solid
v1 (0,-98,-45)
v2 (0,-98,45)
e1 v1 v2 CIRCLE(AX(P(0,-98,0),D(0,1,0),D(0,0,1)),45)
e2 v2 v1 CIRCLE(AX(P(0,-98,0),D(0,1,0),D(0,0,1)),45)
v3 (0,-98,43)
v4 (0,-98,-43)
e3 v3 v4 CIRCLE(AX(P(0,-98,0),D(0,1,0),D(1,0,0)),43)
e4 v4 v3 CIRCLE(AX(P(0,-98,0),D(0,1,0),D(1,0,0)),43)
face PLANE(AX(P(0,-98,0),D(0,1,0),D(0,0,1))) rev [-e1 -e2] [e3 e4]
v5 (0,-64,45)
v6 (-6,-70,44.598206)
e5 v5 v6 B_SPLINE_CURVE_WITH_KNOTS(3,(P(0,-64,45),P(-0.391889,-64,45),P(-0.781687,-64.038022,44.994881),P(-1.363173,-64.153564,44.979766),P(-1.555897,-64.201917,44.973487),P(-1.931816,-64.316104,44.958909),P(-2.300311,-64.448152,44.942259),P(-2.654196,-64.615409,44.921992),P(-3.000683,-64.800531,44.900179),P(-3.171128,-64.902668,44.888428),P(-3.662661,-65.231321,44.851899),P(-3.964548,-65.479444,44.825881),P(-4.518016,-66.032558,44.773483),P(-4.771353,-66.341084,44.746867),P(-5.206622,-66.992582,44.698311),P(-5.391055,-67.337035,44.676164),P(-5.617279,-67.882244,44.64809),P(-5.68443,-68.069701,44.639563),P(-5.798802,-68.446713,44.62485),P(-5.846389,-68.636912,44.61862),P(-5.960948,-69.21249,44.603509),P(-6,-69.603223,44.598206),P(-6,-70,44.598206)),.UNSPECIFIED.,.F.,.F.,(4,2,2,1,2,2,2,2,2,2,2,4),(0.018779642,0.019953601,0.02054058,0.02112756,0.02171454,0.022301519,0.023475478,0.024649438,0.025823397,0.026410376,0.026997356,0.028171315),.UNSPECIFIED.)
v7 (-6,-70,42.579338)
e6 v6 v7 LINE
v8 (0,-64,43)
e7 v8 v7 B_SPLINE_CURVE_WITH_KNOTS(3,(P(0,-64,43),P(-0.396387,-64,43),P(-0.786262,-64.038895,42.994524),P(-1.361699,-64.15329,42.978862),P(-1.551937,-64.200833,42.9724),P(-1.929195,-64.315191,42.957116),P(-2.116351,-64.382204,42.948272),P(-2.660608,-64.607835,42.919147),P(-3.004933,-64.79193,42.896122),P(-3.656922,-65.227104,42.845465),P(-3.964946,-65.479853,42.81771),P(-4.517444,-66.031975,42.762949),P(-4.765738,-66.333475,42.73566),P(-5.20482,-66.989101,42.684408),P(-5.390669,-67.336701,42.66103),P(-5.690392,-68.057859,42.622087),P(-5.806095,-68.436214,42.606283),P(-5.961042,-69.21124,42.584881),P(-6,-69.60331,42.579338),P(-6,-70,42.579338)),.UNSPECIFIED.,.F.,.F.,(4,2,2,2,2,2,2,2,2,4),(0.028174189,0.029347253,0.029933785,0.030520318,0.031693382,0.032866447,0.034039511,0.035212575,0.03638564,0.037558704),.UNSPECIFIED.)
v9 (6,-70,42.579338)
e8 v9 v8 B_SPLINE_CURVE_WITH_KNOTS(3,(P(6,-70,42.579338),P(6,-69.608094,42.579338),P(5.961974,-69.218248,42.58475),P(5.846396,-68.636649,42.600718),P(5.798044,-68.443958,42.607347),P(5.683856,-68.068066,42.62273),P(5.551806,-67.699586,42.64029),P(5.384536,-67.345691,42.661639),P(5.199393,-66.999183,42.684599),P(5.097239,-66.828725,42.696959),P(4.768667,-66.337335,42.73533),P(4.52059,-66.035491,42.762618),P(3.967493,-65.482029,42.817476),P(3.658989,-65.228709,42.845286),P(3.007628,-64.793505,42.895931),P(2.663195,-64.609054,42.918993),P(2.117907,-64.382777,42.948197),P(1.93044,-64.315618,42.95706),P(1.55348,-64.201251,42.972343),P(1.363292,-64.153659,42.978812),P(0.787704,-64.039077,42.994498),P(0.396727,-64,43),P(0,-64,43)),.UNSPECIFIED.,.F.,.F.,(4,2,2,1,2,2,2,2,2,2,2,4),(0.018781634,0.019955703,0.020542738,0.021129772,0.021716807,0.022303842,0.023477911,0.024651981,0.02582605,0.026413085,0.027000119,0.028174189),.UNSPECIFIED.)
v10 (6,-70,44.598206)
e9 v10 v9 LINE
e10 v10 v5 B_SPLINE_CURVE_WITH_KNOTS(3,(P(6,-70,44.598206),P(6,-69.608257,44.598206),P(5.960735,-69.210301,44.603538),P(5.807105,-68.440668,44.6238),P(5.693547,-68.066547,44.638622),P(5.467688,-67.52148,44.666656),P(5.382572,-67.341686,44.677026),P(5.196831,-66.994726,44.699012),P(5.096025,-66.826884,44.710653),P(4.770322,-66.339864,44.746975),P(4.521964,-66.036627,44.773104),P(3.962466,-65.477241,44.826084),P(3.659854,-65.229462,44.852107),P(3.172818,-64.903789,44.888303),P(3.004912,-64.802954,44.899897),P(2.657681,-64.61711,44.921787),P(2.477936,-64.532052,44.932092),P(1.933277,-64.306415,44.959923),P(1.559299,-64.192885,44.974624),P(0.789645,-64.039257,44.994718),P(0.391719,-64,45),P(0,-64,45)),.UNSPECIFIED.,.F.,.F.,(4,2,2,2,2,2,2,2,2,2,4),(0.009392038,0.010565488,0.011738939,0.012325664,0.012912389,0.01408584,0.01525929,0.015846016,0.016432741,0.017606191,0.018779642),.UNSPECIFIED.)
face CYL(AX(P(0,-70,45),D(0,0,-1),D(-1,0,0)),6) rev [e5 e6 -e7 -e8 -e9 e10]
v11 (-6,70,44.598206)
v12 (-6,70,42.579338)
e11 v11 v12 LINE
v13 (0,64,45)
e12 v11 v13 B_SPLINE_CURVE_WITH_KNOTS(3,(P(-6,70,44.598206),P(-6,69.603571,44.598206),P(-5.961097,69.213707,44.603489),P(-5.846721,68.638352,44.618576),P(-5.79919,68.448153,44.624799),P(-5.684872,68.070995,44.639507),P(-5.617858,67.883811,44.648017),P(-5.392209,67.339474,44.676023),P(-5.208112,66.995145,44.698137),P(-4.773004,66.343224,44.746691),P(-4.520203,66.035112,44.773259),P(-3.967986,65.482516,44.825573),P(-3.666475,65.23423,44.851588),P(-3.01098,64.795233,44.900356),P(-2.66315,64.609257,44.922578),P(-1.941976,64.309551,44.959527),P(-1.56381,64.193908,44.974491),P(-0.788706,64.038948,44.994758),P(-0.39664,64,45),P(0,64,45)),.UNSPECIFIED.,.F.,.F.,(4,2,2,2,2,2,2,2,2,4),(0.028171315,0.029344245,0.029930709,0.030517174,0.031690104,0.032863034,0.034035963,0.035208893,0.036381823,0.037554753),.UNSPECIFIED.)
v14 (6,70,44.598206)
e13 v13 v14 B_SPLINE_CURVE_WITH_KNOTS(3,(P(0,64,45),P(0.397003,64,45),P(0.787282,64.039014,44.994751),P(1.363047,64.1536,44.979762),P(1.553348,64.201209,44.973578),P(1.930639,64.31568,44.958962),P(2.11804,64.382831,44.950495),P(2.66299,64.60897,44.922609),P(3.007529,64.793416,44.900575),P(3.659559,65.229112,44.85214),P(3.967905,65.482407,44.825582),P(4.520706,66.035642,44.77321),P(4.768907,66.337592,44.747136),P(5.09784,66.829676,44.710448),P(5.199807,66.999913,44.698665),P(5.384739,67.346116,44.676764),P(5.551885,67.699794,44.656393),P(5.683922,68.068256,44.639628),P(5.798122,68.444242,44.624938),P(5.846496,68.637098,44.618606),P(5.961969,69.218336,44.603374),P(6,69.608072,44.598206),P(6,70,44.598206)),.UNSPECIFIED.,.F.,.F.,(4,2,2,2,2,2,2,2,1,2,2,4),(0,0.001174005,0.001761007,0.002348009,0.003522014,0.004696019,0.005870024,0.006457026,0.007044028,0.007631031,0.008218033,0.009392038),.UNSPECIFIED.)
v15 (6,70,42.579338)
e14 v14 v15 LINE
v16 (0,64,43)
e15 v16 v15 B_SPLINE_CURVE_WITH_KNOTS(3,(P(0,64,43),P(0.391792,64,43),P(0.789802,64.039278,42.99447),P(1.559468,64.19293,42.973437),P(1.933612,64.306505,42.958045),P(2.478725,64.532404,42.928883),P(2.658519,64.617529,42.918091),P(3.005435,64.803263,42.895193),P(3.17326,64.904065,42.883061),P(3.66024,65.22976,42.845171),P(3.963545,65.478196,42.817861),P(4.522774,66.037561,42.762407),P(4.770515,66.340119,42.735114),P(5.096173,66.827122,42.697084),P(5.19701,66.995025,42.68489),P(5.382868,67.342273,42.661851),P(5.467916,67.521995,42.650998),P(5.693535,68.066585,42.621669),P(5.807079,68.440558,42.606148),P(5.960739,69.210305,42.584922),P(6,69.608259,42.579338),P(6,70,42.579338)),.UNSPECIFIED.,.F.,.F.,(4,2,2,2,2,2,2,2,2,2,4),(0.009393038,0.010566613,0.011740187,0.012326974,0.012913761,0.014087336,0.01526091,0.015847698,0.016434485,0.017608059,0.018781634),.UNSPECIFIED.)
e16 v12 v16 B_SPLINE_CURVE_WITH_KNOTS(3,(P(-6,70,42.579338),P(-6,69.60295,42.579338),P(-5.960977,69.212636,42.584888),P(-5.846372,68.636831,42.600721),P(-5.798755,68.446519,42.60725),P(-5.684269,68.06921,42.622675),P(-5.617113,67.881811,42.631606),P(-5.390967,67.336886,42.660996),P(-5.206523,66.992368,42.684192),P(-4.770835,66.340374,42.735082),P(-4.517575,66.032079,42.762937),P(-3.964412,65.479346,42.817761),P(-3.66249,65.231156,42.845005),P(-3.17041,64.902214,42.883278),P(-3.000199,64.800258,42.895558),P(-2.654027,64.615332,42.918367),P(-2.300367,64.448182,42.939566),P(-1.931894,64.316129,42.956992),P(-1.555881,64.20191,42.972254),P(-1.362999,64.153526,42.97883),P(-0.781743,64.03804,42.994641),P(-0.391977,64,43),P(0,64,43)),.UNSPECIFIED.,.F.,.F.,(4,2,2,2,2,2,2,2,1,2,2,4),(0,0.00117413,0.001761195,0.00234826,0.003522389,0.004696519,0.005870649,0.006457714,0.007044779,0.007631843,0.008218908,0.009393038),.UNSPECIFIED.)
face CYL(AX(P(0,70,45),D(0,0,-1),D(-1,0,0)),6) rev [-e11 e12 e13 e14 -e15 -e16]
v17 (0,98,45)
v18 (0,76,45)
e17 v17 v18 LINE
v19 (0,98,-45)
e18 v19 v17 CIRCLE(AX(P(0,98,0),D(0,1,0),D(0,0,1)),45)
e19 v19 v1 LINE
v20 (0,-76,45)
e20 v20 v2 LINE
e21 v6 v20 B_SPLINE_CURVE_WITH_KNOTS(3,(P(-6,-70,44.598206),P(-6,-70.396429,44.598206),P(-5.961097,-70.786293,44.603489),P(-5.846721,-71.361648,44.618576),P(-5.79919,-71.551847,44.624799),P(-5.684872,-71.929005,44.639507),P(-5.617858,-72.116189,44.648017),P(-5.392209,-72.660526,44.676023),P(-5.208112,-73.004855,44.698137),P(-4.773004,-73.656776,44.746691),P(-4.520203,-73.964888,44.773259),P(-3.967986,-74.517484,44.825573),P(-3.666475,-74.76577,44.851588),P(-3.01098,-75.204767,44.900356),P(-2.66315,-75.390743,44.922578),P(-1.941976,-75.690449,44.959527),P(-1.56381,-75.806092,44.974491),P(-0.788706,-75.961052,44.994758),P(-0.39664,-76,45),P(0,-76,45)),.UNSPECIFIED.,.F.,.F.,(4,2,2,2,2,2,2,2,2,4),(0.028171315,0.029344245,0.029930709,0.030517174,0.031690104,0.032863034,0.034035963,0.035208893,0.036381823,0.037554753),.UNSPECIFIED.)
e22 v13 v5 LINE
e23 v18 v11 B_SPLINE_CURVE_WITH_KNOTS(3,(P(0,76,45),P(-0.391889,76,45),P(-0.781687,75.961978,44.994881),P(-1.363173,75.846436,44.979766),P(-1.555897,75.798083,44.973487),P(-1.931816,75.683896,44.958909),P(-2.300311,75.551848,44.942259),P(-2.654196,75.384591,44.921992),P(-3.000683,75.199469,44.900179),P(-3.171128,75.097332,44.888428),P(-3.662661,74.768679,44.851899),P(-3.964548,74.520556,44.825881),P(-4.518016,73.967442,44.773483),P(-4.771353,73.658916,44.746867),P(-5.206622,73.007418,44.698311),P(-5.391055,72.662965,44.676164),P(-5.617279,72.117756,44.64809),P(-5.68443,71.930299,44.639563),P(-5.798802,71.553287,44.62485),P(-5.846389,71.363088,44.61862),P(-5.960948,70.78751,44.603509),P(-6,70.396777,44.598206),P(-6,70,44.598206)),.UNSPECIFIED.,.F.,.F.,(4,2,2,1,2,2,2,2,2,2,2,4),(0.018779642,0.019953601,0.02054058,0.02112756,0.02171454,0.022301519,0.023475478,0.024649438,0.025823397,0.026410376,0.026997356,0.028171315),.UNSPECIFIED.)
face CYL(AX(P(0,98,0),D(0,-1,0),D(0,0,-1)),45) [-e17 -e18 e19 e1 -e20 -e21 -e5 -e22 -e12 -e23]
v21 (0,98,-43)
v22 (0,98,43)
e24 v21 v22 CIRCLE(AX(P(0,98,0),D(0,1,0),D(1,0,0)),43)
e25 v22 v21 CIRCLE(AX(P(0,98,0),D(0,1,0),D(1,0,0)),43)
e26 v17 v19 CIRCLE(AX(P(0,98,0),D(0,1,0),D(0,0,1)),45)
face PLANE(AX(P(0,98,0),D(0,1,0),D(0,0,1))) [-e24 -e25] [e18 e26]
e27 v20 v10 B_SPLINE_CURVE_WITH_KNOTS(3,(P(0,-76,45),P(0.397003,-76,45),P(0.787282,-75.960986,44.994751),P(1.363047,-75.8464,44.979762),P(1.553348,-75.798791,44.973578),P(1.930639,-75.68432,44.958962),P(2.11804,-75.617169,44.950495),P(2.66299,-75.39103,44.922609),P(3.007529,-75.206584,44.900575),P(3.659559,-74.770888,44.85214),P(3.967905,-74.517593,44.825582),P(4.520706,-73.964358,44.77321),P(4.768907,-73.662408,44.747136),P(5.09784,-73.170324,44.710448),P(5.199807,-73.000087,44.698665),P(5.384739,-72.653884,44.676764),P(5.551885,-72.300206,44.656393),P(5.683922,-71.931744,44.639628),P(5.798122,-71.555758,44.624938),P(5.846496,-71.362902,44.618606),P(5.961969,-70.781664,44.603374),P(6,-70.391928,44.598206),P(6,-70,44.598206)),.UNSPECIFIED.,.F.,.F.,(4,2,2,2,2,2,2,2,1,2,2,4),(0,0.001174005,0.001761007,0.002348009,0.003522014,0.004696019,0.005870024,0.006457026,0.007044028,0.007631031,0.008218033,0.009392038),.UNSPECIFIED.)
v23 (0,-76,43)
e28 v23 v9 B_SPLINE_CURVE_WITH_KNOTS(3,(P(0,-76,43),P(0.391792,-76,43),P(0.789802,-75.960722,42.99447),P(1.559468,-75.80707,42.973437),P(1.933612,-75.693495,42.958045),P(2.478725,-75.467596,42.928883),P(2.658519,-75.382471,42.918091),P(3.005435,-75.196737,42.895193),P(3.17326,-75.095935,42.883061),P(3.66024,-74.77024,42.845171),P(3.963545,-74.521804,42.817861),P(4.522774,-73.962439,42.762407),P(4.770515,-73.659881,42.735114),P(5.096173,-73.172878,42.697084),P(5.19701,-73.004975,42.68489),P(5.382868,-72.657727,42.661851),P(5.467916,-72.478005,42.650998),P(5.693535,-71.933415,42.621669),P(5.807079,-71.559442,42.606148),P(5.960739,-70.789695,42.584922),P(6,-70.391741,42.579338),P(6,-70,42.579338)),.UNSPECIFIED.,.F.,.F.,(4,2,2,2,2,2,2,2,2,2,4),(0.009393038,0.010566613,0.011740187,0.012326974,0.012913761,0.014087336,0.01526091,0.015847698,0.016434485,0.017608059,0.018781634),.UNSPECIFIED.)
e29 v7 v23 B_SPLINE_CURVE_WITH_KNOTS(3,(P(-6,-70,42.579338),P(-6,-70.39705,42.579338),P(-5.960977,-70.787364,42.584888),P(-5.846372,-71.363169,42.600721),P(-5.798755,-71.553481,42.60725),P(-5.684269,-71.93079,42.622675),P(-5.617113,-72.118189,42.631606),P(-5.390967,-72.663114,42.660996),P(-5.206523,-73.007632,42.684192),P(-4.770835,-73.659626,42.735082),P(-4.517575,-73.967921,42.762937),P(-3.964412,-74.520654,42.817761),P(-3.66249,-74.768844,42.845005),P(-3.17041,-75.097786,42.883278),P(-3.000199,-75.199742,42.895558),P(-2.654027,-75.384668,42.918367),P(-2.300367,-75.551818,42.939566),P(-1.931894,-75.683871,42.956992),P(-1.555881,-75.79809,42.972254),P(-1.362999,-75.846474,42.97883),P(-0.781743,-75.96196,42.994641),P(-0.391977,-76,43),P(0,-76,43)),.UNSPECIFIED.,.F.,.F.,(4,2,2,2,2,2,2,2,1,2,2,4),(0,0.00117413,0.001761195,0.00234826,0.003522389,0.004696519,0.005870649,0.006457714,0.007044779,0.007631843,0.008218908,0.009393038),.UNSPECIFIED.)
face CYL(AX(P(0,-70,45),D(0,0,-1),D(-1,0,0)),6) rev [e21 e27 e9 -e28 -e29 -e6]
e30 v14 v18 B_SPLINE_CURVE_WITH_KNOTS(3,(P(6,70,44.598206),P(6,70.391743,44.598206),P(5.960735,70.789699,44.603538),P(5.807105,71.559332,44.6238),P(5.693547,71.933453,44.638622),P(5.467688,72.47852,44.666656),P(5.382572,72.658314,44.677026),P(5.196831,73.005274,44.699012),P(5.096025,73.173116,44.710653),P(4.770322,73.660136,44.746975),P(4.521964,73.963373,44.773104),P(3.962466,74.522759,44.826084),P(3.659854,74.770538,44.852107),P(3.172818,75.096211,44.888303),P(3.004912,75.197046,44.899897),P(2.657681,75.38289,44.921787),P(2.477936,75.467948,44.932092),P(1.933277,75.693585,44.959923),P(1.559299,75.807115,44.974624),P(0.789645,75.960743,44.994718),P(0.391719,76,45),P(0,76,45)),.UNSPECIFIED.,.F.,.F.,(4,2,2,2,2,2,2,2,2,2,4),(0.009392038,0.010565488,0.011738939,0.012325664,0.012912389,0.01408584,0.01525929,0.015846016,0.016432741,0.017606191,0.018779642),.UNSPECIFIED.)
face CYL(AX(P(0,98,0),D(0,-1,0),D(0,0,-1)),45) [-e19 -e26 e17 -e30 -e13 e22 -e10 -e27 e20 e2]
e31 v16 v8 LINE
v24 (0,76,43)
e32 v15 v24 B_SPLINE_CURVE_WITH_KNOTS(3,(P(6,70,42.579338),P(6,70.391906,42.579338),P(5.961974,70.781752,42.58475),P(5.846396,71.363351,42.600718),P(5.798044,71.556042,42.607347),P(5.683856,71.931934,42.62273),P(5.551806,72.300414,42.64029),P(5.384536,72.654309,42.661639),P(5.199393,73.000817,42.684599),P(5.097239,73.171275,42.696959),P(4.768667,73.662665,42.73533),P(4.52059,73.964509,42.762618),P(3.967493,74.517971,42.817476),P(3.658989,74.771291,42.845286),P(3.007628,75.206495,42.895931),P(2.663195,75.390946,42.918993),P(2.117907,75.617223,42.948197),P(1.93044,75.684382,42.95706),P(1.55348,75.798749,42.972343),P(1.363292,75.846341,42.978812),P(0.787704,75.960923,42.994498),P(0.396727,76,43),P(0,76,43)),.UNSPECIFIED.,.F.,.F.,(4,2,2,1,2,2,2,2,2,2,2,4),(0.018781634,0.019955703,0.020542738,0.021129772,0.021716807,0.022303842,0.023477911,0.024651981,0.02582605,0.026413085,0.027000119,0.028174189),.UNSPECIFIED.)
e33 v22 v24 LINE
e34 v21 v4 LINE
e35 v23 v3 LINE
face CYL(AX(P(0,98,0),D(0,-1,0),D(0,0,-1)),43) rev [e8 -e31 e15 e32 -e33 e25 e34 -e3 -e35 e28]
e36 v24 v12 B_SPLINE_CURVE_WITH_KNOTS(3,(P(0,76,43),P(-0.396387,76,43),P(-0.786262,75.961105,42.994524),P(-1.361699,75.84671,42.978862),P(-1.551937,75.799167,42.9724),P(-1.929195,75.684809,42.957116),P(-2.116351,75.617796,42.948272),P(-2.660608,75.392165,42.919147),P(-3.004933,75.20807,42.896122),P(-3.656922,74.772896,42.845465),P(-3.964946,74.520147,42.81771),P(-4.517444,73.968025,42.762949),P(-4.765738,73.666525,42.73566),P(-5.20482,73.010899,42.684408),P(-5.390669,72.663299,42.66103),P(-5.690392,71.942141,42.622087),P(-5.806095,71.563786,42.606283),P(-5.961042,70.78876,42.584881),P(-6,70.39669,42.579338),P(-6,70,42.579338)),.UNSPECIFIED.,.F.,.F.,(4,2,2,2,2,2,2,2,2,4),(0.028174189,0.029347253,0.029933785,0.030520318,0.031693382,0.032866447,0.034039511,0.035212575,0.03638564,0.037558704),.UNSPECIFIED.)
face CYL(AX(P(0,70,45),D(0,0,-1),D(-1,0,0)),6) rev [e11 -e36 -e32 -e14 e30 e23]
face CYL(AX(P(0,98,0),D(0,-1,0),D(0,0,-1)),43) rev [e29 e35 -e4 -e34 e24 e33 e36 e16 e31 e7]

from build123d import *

# Parameters (mm, degrees)
SKETCH_2_R          = 45
SKETCH_2_R_2        = 43
EXTRUDE_1_DEPTH     = 98
SKETCH_3_R          = 6
CUT_EXTRUDE_2_DEPTH = 117.850331621


with BuildPart() as part:
    # 草图2 → 拉伸-薄壁1 (new, symmetric)
    with BuildSketch(Plane(origin=(0, 0, 0), x_dir=(1, 0, 0), z_dir=(0, 1, 0))):
        Circle(SKETCH_2_R)
        Circle(SKETCH_2_R_2, mode=Mode.SUBTRACT)
    extrude(amount=EXTRUDE_1_DEPTH, both=True)

    # 草图3 → 切除-拉伸2 (cut, through all)
    with BuildSketch(Plane.XY):
        with Locations(Location((0, 70, 0), (0, 0, 180))):
            Circle(SKETCH_3_R)
        with Locations(Location((0, -70, 0), (0, 0, 180))):
            Circle(SKETCH_3_R)
    extrude(amount=CUT_EXTRUDE_2_DEPTH, mode=Mode.SUBTRACT)


solid = part.part
